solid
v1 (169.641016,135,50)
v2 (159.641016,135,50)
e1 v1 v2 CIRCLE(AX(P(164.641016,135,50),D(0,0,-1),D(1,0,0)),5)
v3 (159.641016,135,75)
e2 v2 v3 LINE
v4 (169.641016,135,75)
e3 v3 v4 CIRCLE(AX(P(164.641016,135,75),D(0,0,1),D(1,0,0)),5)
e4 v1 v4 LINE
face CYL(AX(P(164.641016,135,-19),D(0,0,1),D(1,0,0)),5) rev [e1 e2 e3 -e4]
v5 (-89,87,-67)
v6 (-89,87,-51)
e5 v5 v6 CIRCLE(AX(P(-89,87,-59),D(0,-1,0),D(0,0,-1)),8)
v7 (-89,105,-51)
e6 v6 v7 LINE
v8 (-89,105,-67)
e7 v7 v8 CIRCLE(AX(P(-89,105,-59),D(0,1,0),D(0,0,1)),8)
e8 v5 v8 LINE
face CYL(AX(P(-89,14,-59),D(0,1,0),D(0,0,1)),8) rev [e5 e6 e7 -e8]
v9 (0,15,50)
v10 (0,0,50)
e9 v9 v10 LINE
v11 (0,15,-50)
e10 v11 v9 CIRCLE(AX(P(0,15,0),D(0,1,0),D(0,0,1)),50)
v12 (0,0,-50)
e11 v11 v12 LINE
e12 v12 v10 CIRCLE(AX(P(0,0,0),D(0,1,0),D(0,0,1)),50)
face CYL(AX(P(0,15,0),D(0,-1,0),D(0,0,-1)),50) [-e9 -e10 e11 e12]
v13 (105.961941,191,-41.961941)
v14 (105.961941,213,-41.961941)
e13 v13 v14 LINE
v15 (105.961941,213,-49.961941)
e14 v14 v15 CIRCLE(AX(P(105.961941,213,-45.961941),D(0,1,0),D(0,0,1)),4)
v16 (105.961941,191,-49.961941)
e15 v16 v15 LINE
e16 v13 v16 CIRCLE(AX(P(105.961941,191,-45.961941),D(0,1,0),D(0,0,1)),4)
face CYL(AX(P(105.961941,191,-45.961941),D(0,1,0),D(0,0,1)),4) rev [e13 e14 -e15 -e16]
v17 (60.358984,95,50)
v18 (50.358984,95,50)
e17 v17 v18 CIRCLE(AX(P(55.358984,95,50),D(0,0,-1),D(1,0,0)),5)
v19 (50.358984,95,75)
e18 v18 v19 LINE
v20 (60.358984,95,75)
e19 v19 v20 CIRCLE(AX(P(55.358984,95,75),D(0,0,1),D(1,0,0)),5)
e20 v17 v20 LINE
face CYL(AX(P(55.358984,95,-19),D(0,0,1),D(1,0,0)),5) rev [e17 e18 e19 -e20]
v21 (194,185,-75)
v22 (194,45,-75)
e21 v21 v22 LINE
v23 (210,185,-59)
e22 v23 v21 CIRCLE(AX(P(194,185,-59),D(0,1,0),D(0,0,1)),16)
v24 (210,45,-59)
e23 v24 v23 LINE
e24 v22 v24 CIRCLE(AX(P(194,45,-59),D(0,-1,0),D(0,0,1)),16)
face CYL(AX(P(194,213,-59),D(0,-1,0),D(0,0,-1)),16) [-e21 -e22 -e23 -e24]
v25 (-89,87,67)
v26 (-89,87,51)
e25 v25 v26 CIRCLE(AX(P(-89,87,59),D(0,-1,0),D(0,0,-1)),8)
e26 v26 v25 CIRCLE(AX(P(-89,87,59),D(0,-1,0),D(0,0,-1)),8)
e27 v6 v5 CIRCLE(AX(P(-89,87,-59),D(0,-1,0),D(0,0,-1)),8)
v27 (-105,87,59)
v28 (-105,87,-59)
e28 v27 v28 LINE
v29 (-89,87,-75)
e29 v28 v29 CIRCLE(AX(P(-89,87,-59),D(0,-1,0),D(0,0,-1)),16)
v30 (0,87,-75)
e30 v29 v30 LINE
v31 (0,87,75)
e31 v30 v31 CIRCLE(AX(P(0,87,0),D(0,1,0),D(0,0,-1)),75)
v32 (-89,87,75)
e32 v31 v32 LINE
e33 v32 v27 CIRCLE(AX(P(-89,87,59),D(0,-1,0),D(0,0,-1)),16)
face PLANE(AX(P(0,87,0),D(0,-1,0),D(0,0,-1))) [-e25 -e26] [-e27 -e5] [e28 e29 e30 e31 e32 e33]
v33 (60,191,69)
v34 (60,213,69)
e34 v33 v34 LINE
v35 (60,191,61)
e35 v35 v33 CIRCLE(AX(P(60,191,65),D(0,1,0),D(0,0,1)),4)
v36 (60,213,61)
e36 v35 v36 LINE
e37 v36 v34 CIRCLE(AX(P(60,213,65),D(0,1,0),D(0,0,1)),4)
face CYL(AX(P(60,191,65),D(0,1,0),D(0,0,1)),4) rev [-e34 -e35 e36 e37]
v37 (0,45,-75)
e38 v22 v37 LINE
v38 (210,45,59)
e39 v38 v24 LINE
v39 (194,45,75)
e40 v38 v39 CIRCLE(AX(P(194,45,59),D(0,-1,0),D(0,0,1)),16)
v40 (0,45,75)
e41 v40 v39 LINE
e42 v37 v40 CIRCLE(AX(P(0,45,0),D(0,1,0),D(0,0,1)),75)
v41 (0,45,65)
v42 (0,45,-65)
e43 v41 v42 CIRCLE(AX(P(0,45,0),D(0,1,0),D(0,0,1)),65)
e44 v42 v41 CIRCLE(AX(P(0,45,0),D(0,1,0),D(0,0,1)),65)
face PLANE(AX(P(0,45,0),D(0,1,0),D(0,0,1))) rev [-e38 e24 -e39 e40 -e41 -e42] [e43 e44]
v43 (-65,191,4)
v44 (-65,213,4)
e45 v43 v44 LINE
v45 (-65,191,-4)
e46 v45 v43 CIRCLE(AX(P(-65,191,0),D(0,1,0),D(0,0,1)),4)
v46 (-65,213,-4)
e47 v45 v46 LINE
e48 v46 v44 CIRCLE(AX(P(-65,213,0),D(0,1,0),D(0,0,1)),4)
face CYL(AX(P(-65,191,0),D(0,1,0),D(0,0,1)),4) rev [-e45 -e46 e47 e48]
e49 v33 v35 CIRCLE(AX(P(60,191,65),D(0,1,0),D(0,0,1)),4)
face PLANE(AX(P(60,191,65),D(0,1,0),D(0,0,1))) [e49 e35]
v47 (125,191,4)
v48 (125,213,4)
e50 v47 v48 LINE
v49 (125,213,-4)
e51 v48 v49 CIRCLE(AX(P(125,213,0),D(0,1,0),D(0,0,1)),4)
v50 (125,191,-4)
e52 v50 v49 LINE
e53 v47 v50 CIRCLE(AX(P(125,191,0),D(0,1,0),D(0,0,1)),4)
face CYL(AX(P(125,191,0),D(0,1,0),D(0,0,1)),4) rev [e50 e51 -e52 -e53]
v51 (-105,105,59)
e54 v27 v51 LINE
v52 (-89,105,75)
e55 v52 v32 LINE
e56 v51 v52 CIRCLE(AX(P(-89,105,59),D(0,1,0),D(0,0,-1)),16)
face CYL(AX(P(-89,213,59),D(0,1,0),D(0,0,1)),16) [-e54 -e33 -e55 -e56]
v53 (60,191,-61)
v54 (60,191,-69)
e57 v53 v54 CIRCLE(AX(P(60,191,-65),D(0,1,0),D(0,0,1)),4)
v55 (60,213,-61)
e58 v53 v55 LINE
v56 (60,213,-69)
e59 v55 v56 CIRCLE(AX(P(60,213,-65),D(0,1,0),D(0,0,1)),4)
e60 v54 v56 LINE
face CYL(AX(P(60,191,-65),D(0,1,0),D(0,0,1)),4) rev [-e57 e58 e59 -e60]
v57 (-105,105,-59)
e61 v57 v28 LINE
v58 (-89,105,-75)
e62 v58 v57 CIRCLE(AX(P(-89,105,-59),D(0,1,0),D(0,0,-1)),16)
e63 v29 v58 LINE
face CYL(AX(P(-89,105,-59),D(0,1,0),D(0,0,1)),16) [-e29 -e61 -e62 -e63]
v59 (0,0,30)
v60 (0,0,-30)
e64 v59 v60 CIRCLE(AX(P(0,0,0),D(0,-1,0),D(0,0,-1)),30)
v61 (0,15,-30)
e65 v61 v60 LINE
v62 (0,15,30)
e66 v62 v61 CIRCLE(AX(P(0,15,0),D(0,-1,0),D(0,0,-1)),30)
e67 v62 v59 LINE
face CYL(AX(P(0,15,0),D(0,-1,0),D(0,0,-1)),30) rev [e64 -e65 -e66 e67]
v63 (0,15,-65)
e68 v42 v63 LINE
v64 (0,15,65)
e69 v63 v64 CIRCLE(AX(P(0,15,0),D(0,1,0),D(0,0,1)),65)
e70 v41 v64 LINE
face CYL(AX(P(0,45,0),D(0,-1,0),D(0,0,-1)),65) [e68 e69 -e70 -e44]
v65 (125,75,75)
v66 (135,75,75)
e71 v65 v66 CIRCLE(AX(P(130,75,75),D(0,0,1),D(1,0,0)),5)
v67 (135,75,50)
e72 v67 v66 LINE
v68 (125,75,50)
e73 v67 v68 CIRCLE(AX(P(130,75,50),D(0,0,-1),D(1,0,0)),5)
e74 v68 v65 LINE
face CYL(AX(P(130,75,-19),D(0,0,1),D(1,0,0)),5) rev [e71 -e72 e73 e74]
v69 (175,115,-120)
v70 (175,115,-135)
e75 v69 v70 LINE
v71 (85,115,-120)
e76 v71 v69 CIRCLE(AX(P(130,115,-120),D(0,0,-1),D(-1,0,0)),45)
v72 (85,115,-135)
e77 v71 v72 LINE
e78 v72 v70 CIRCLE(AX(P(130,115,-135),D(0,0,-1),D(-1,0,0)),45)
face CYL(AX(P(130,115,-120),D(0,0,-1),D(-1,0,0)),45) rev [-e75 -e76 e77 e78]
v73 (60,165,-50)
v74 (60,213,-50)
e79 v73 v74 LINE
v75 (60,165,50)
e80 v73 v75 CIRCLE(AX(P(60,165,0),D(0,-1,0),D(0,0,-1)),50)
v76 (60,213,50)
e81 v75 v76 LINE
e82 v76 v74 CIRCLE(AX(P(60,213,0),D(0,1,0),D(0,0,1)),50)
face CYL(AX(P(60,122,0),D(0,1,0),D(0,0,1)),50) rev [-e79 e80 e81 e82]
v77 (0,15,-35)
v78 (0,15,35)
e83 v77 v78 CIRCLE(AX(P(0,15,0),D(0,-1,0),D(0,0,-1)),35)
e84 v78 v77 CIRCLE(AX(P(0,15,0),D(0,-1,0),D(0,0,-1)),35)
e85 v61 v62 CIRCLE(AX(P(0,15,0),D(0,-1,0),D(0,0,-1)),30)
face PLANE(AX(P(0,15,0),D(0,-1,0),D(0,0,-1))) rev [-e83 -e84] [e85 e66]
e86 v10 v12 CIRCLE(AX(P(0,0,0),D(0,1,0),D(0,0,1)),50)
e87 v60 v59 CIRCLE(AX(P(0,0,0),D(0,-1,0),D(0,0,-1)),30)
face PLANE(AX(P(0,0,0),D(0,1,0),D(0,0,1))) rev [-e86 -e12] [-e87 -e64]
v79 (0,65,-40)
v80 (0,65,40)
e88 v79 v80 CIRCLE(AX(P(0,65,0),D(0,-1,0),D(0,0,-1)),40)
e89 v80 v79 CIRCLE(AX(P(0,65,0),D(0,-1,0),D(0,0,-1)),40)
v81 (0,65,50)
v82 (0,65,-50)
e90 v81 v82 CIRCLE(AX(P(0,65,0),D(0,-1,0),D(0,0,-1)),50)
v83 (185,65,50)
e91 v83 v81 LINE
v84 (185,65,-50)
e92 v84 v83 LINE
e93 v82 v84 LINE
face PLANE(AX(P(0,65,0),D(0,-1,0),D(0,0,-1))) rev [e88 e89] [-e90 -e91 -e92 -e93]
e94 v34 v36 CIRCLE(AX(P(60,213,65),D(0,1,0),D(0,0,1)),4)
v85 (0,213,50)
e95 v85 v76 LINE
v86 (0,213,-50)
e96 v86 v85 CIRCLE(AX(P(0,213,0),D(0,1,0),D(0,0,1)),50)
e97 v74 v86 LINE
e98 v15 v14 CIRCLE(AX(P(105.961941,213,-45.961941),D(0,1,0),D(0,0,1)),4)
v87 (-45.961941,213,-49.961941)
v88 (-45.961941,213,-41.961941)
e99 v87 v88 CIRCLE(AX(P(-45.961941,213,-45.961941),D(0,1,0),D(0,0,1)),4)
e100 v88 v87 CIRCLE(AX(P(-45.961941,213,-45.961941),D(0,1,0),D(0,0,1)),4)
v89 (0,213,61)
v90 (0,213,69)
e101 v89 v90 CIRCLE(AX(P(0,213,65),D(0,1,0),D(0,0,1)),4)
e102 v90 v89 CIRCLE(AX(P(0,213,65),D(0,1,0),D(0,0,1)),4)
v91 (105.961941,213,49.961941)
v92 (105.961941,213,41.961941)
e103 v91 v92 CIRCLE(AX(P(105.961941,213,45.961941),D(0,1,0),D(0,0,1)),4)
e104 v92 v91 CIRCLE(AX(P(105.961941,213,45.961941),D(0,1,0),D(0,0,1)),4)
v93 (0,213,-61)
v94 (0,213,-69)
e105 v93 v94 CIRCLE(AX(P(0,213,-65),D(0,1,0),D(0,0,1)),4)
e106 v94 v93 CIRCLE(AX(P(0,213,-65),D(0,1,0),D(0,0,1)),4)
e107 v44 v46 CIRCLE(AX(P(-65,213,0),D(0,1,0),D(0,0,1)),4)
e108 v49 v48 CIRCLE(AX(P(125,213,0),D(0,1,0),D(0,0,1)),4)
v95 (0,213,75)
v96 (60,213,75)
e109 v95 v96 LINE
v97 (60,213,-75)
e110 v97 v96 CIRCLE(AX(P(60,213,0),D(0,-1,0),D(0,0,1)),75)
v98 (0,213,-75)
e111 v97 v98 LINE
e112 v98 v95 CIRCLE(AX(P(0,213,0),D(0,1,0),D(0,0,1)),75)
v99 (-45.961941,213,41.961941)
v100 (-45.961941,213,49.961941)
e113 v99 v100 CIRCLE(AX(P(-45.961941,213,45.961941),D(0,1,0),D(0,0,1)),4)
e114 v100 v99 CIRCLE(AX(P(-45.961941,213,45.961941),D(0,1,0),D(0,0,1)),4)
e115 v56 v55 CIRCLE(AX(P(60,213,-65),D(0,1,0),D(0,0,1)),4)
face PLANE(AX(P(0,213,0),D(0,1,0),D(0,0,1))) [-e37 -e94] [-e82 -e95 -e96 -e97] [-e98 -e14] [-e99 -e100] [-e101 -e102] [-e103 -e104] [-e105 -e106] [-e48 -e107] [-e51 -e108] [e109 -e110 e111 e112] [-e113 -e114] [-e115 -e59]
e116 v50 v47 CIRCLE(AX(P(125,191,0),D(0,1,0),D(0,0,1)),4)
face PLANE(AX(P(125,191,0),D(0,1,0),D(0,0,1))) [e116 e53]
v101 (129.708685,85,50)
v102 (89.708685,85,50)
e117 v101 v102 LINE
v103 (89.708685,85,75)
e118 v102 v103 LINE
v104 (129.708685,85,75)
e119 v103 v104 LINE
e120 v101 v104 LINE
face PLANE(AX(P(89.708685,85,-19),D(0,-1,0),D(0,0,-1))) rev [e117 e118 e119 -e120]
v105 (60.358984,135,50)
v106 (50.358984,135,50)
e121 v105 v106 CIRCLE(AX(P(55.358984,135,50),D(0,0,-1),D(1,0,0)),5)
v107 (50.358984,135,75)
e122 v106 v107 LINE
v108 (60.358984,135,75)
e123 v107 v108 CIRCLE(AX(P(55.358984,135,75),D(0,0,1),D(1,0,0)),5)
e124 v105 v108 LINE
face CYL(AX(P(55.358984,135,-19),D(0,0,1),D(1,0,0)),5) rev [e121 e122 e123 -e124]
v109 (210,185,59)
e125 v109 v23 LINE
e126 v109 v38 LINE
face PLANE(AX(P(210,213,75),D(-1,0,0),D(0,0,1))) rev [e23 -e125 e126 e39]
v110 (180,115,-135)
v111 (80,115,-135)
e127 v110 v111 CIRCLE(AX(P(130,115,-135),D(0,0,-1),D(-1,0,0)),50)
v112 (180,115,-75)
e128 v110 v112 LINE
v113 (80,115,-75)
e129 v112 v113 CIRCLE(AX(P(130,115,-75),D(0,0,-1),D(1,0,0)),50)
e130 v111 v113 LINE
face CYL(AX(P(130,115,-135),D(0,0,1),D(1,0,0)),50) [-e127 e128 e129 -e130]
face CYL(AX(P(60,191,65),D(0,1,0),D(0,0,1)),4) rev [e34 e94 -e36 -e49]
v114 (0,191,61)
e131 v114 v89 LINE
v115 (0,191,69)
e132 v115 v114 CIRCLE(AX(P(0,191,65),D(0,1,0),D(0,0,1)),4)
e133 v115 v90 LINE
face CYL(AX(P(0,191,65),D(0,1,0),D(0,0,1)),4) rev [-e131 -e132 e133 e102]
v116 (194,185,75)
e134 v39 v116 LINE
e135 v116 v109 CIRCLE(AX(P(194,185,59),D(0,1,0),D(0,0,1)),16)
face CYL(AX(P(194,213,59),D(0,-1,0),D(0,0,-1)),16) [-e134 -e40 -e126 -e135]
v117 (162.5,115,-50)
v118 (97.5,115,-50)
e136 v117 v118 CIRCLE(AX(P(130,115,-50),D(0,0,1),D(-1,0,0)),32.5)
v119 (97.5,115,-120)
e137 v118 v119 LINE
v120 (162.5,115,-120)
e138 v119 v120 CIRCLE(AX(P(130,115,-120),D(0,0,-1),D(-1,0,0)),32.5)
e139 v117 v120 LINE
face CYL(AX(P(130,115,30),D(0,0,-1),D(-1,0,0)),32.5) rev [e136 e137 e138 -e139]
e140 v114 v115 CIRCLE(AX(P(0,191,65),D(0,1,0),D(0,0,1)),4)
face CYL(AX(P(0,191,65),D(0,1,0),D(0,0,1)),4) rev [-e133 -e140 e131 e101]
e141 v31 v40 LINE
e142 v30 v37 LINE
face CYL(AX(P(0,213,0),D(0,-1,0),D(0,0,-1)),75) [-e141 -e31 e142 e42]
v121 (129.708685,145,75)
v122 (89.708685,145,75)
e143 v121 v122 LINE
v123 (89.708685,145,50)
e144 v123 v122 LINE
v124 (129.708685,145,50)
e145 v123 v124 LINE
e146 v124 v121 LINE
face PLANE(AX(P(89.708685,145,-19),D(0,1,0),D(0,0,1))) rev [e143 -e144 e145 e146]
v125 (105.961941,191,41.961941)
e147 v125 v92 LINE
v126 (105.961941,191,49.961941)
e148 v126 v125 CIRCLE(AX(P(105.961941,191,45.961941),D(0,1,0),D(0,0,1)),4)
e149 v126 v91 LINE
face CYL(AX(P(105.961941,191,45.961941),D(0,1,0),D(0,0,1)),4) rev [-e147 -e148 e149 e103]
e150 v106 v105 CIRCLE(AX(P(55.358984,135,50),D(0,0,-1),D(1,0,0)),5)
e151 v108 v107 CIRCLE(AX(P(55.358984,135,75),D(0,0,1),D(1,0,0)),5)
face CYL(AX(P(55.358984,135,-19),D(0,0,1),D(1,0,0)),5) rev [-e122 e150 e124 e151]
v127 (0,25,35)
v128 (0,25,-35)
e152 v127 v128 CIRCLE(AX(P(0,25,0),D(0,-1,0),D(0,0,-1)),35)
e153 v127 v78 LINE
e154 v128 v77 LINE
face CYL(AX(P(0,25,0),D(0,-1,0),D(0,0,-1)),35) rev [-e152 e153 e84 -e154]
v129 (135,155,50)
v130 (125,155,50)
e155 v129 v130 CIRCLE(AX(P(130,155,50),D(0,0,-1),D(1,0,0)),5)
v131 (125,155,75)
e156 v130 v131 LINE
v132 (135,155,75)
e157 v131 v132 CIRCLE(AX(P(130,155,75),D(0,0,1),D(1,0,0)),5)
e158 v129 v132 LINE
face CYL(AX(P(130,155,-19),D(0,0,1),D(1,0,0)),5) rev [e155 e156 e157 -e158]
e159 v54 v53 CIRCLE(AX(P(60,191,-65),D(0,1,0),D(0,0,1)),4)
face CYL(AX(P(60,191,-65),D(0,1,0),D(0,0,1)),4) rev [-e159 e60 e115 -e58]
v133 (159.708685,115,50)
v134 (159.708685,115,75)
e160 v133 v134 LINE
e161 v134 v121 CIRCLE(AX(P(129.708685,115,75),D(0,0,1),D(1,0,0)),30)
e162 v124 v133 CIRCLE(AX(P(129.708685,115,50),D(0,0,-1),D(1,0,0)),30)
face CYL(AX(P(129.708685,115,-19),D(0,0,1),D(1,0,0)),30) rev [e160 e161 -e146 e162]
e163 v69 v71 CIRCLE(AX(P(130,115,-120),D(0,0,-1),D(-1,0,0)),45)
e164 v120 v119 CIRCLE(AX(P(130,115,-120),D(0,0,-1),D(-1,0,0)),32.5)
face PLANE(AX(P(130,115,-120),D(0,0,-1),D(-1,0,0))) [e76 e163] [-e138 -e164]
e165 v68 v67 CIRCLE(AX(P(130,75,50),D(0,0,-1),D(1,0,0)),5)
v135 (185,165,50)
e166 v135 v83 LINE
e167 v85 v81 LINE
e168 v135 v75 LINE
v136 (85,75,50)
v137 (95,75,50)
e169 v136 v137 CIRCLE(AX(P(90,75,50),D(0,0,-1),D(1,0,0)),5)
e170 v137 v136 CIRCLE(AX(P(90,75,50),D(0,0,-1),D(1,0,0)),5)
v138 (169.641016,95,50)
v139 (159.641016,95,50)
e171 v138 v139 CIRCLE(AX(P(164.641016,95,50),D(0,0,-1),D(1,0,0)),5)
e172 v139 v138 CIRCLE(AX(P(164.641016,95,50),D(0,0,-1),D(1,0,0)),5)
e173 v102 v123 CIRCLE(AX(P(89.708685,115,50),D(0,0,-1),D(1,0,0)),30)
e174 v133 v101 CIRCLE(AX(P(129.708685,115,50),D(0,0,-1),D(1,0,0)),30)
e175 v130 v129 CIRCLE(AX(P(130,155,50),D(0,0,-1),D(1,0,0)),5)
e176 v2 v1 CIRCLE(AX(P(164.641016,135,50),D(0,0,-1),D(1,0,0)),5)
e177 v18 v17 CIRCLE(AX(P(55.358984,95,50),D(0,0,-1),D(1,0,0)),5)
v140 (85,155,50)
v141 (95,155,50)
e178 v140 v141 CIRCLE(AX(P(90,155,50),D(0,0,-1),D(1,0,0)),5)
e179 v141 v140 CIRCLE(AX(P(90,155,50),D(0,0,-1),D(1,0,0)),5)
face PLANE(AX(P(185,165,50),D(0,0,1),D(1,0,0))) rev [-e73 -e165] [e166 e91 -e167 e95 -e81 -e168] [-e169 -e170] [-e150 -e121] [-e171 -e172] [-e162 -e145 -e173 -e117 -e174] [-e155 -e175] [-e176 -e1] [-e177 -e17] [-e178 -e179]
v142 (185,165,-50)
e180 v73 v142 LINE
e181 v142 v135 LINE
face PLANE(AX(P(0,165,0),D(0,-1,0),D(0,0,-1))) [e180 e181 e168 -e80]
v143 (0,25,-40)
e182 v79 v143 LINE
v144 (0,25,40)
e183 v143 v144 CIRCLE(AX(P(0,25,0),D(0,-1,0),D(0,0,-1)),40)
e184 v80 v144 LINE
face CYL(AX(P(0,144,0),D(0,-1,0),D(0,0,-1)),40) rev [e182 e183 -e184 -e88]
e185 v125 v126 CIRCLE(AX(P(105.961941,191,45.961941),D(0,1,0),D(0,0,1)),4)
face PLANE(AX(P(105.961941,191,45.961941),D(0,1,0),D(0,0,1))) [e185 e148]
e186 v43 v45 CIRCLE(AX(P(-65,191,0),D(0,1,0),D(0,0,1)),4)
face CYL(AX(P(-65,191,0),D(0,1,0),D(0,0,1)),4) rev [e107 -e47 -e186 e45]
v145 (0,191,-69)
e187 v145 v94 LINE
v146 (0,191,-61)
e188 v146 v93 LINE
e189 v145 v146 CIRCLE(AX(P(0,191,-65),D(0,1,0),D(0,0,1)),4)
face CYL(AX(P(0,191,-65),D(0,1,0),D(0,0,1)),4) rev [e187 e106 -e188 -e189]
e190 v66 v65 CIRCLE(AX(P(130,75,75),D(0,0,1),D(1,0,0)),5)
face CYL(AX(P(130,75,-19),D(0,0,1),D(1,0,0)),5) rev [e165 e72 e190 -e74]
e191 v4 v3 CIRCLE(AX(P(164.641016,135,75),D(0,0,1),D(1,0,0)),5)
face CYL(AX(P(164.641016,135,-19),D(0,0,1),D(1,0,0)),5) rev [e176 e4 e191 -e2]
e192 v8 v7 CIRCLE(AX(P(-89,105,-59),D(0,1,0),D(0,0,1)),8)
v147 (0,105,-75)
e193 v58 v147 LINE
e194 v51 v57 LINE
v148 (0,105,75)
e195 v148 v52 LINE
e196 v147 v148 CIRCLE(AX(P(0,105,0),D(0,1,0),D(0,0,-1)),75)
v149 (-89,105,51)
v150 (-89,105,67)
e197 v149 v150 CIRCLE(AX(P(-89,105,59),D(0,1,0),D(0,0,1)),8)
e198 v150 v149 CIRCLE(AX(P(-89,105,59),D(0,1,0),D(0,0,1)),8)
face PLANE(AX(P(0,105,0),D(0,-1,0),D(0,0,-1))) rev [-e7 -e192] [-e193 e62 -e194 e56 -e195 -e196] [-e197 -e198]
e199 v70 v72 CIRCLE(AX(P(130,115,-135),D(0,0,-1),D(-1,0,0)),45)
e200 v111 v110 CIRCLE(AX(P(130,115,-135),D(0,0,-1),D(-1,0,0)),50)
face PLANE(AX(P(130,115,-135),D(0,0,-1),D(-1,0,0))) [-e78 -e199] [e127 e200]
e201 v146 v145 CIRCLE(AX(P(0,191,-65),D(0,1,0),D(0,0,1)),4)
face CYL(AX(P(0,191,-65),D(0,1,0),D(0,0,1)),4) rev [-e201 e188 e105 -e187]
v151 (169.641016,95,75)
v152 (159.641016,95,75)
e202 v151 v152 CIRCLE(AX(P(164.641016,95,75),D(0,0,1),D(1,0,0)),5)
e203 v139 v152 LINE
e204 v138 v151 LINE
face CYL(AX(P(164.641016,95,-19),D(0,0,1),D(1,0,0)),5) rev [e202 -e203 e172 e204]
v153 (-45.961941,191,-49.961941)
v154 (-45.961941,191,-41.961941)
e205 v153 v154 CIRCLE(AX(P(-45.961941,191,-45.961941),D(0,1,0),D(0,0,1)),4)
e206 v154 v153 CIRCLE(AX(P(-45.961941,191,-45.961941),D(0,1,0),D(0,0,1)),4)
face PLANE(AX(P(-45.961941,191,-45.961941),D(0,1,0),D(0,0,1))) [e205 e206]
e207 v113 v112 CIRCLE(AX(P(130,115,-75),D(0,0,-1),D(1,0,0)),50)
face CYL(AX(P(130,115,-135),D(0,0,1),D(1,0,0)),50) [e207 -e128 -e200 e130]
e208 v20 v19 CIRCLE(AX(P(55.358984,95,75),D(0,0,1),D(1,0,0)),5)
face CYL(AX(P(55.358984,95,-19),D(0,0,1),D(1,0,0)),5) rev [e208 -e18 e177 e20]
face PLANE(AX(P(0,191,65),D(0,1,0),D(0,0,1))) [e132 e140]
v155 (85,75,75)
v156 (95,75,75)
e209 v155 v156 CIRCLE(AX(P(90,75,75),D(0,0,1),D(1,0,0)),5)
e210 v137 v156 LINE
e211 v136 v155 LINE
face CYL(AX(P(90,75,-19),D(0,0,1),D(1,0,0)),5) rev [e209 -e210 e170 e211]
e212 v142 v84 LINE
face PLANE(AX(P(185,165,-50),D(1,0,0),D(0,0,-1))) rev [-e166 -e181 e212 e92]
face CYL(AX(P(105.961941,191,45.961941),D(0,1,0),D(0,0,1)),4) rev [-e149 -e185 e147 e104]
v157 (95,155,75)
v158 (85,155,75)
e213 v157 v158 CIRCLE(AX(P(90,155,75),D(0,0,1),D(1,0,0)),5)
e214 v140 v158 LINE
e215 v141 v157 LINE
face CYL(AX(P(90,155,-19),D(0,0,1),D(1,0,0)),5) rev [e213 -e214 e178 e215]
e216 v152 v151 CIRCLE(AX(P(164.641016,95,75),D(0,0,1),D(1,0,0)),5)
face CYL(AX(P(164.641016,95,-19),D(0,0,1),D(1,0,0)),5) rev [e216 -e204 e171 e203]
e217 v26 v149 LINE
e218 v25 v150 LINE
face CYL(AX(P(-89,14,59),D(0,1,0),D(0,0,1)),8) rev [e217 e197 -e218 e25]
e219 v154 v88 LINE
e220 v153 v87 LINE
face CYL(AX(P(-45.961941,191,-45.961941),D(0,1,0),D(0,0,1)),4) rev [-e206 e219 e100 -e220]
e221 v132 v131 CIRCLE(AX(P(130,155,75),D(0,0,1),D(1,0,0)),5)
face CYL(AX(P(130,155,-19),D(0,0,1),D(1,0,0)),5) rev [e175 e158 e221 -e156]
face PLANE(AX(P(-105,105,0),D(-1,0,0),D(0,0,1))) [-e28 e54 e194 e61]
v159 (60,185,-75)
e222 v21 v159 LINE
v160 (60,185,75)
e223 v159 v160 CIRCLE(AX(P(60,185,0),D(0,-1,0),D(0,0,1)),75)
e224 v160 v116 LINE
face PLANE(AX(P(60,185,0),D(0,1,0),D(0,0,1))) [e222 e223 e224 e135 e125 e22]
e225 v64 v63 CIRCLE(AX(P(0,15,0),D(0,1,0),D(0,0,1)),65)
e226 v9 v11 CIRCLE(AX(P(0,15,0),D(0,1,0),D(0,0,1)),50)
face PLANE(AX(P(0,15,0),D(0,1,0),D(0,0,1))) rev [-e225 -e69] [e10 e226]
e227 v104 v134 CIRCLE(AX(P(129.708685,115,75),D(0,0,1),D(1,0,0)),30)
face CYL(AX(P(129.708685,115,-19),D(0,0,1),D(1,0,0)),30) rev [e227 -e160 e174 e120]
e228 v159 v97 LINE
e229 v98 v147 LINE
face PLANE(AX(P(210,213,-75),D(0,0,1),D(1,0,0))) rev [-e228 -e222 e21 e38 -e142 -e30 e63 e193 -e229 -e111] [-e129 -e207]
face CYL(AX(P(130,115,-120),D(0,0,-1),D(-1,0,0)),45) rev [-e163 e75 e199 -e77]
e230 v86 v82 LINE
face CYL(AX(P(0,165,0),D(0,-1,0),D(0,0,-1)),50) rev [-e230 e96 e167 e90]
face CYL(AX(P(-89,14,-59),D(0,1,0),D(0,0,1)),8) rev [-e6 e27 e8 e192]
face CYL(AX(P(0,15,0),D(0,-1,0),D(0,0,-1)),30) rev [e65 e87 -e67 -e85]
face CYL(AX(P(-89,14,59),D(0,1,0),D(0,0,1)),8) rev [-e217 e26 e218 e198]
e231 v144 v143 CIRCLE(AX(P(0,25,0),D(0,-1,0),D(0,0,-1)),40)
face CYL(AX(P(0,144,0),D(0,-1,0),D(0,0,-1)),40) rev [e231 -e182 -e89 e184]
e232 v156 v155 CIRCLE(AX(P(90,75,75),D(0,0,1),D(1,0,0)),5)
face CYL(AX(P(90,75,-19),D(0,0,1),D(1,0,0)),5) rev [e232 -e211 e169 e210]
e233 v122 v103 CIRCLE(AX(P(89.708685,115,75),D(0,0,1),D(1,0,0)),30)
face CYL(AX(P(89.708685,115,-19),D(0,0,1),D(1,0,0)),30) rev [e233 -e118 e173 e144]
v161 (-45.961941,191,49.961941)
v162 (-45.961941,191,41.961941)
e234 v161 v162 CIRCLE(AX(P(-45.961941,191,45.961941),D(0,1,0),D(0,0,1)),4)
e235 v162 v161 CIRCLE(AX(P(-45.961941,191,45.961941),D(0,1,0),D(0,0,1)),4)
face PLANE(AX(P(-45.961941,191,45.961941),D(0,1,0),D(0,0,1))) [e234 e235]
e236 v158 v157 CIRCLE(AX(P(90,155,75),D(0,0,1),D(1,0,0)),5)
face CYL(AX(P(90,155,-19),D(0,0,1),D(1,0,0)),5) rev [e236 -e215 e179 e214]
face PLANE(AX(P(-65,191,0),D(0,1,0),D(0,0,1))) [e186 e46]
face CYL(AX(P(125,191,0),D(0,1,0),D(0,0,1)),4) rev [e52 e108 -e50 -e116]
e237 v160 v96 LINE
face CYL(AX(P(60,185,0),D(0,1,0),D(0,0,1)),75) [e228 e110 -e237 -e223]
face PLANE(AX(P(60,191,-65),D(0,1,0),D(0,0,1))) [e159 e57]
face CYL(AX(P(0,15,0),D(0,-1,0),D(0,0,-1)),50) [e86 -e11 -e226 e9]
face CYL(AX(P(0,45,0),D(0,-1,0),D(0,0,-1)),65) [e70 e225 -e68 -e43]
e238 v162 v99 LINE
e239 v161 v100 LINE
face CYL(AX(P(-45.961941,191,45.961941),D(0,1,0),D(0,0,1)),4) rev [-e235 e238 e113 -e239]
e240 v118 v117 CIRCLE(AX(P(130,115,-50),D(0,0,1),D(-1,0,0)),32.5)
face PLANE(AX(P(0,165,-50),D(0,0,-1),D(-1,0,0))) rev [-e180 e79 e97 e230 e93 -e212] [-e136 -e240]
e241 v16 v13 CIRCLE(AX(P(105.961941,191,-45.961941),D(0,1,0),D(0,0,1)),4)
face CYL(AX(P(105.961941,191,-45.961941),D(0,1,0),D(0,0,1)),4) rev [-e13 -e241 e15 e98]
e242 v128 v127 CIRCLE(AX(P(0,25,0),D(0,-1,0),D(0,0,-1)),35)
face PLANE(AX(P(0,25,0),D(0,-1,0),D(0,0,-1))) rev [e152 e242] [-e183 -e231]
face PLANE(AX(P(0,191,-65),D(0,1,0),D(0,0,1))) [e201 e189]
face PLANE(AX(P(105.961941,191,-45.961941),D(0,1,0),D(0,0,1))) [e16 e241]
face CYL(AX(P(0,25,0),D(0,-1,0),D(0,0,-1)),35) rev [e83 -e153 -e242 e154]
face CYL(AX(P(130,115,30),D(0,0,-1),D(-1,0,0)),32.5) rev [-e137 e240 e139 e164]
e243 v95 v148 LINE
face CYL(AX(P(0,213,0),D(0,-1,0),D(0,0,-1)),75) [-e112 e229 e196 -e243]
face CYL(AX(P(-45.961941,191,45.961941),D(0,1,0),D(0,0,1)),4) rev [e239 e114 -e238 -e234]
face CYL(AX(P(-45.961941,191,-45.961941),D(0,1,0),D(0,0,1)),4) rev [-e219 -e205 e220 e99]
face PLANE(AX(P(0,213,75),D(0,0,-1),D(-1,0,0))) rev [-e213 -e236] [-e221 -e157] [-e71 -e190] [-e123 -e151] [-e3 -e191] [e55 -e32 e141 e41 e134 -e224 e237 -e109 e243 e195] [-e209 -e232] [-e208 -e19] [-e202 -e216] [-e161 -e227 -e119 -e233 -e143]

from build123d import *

# Parameters (mm, degrees)
BASE_BOSS_SKETCH_R         = 50
BASE_BOSS_100_DEPTH        = 15
BEARING_BOSS_SKETCH_R      = 65
BEARING_BOSS_130_DEPTH     = 30
HOUSING_BLOCK_75X210_DEPTH = 168
HOUSING_RECESS_CUT_DEPTH   = 28
MOUNTING_FLANGE_DEPTH      = 18
GEAR_CAVITY_SKETCH_R       = 5
GEAR_CAVITY_CUT_DEPTH      = 94
CAVITY_RELIEF_CUT_DEPTH    = 94
PORT_BOSS_SKETCH_R         = 50
PORT_BOSS_100_DEPTH        = 60
PORT_COUNTERBORE_SKETCH_R  = 45
PORT_COUNTERBORE_90_DEPTH  = 15
PORT_BORE_SKETCH_R         = 32.5
PORT_BORE_65_DEPTH         = 150
SIDE_POCKET_50X185_DEPTH   = 50
BASE_BORE_SKETCH_R         = 30
BASE_BORE_60_DEPTH         = 15
BASE_COUNTERBORE_SKETCH_R  = 35
BASE_COUNTERBORE_70_DEPTH  = 10
SHAFT_BORE_SKETCH_R        = 40
SHAFT_BORE_80_DEPTH        = 119
COVER_BOLT_HOLES_SKETCH_R  = 4
COVER_BOLT_HOLES_8_DEPTH   = 22
FLANGE_FILLET_R16_A_R      = 16
FLANGE_FILLET_R16_B_R      = 16
FLANGE_BOLT_HOLES_SKETCH_R = 8
FLANGE_BOLT_HOLES_16_DEPTH = 91
INNER_START                = -91
INNER_SLOT_CUT_DEPTH       = 91
HOUSING_FILLET_R16_A_R     = 16
HOUSING_FILLET_R16_B_R     = 16


with BuildPart() as part:
    # Base Boss Sketch → Base Boss Ø100 (new body)
    with BuildSketch(Plane(origin=(0, 0, 0), x_dir=(1, 0, 0), z_dir=(0, 1, 0))):
        with Locations(Location((0, 0, 0), (0, 0, 270))):
            Circle(BASE_BOSS_SKETCH_R)
    extrude(amount=BASE_BOSS_100_DEPTH)

    # Bearing Boss Sketch → Bearing Boss Ø130 (add)
    with BuildSketch(Plane(origin=(0, 15, 0), x_dir=(1, 0, 0), z_dir=(0, 1, 0))):
        with Locations(Location((0, 0, 0), (0, 0, 270))):
            Circle(BEARING_BOSS_SKETCH_R)
    extrude(amount=BEARING_BOSS_130_DEPTH)

    # Housing Block Sketch → Housing Block 75x210 (add)
    with BuildSketch(Plane(origin=(0, 45, 0), x_dir=(1, 0, 0), z_dir=(0, 1, 0))):
        with BuildLine():
            Line((0, -75), (210, -75))
            Line((210, -75), (210, 75))
            Line((210, 75), (0, 75))
            ThreePointArc((0, 75), (-75, 0), (0, -75))
        make_face()
    extrude(amount=HOUSING_BLOCK_75X210_DEPTH)

    # Housing Recess Sketch → Housing Recess Cut (cut)
    with BuildSketch(Plane(origin=(0, 213, 0), x_dir=(1, 0, 0), z_dir=(0, 1, 0))):
        with BuildLine():
            Line((60, 75), (210, 75))
            Line((210, 75), (210, -75))
            Line((210, -75), (60, -75))
            ThreePointArc((60, -75), (135, 0), (60, 75))
        make_face()
    extrude(amount=-HOUSING_RECESS_CUT_DEPTH, mode=Mode.SUBTRACT)

    # Mounting Flange Sketch → Mounting Flange (add)
    with BuildSketch(Plane(origin=(0, 87, 0), x_dir=(-1, 0, 0), z_dir=(0, -1, 0))):
        with BuildLine():
            Line((105, 0), (105, 75))
            Line((105, 75), (0, 75))
            ThreePointArc((0, 75), (75, 0), (0, -75))
            Line((0, -75), (105, -75))
            Line((105, -75), (105, 0))
        make_face()
    extrude(amount=-MOUNTING_FLANGE_DEPTH)

    # Gear Cavity Sketch → Gear Cavity Cut (cut)
    with BuildSketch(Plane.XY.offset(75)):
        with Locations((130, 155)):
            Circle(GEAR_CAVITY_SKETCH_R)
        with Locations((90, 155)):
            Circle(GEAR_CAVITY_SKETCH_R)
        with Locations((164.641016151, 135)):
            Circle(GEAR_CAVITY_SKETCH_R)
        with Locations((164.641016151, 95)):
            Circle(GEAR_CAVITY_SKETCH_R)
        with Locations((130, 75)):
            Circle(GEAR_CAVITY_SKETCH_R)
        with Locations((90, 75)):
            Circle(GEAR_CAVITY_SKETCH_R)
        with Locations((55.358983849, 95)):
            Circle(GEAR_CAVITY_SKETCH_R)
        with Locations((55.358983849, 135)):
            Circle(GEAR_CAVITY_SKETCH_R)
    extrude(amount=-GEAR_CAVITY_CUT_DEPTH, mode=Mode.SUBTRACT)

    # Cavity Relief Sketch → Cavity Relief Cut (cut)
    with BuildSketch(Plane.XY.offset(75)):
        with BuildLine():
            Line((89.708684664, 145), (129.708684664, 145))
            ThreePointArc((129.708684664, 145), (159.708684664, 115), (129.708684664, 85))
            Line((129.708684664, 85), (89.708684664, 85))
            ThreePointArc((89.708684664, 85), (59.708684664, 115), (89.708684664, 145))
        make_face()
    extrude(amount=-CAVITY_RELIEF_CUT_DEPTH, mode=Mode.SUBTRACT)

    # Port Boss Sketch → Port Boss Ø100 (add)
    with BuildSketch(Plane(origin=(0, 0, -75), x_dir=(-1, 0, 0), z_dir=(0, 0, -1))):
        with Locations(Location((-130, 115, 0), (0, 0, 180))):
            Circle(PORT_BOSS_SKETCH_R)
    extrude(amount=PORT_BOSS_100_DEPTH)

    # Port Counterbore Sketch → Port Counterbore Ø90 (cut)
    with BuildSketch(Plane(origin=(0, 0, -135), x_dir=(-1, 0, 0), z_dir=(0, 0, -1))):
        with Locations((-130, 115)):
            Circle(PORT_COUNTERBORE_SKETCH_R)
    extrude(amount=-PORT_COUNTERBORE_90_DEPTH, mode=Mode.SUBTRACT)

    # Port Bore Sketch → Port Bore Ø65 (cut)
    with BuildSketch(Plane(origin=(0, 0, -120), x_dir=(-1, 0, 0), z_dir=(0, 0, -1))):
        with Locations((-130, 115)):
            Circle(PORT_BORE_SKETCH_R)
    extrude(amount=-PORT_BORE_65_DEPTH, mode=Mode.SUBTRACT)

    # Side Pocket Sketch → Side Pocket 50x185 (cut, symmetric)
    with BuildSketch(Plane(origin=(0, 115, 0), x_dir=(-1, 0, 0), z_dir=(0, -1, 0))):
        with BuildLine():
            Line((0, 50), (-185, 50))
            Line((-185, 50), (-185, -50))
            Line((-185, -50), (0, -50))
            ThreePointArc((0, -50), (50, 0), (0, 50))
        make_face()
    extrude(amount=SIDE_POCKET_50X185_DEPTH, both=True, mode=Mode.SUBTRACT)

    # Base Bore Sketch → Base Bore Ø60 (cut)
    with BuildSketch(Plane.XZ):
        with Locations(Location((0, 0, 0), (0, 0, 270))):
            Circle(BASE_BORE_SKETCH_R)
    extrude(amount=-BASE_BORE_60_DEPTH, mode=Mode.SUBTRACT)

    # Base Counterbore Sketch → Base Counterbore Ø70 (cut)
    with BuildSketch(Plane.XZ.offset(-15)):
        with Locations(Location((0, 0, 0), (0, 0, 270))):
            Circle(BASE_COUNTERBORE_SKETCH_R)
    extrude(amount=-BASE_COUNTERBORE_70_DEPTH, mode=Mode.SUBTRACT)

    # Shaft Bore Sketch → Shaft Bore Ø80 (cut)
    with BuildSketch(Plane.XZ.offset(-25)):
        with Locations(Location((0, 0, 0), (0, 0, 270))):
            Circle(SHAFT_BORE_SKETCH_R)
    extrude(amount=-SHAFT_BORE_80_DEPTH, mode=Mode.SUBTRACT)

    # Cover Bolt Holes Sketch → Cover Bolt Holes Ø8 (cut)
    with BuildSketch(Plane(origin=(0, 213, 0), x_dir=(1, 0, 0), z_dir=(0, 1, 0))):
        with Locations(Location((125, 0, 0), (0, 0, 270))):
            Circle(COVER_BOLT_HOLES_SKETCH_R)
        with Locations(Location((105.961940777, 45.961940777, 0), (0, 0, 270))):
            Circle(COVER_BOLT_HOLES_SKETCH_R)
        with Locations(Location((105.961940777, -45.961940777, 0), (0, 0, 270))):
            Circle(COVER_BOLT_HOLES_SKETCH_R)
        with Locations(Location((60, -65, 0), (0, 0, 270))):
            Circle(COVER_BOLT_HOLES_SKETCH_R)
        with Locations(Location((0, -65, 0), (0, 0, 270))):
            Circle(COVER_BOLT_HOLES_SKETCH_R)
        with Locations(Location((-45.961940777, -45.961940777, 0), (0, 0, 270))):
            Circle(COVER_BOLT_HOLES_SKETCH_R)
        with Locations(Location((-45.961940777, 45.961940777, 0), (0, 0, 270))):
            Circle(COVER_BOLT_HOLES_SKETCH_R)
        with Locations(Location((0, 65, 0), (0, 0, 270))):
            Circle(COVER_BOLT_HOLES_SKETCH_R)
        with Locations(Location((60, 65, 0), (0, 0, 270))):
            Circle(COVER_BOLT_HOLES_SKETCH_R)
        with Locations(Location((-65, 0, 0), (0, 0, 270))):
            Circle(COVER_BOLT_HOLES_SKETCH_R)
    extrude(amount=-COVER_BOLT_HOLES_8_DEPTH, mode=Mode.SUBTRACT)

    # Flange Fillet R16 A
    flange_fillet_r16_a_edges = [part.edges().sort_by_distance(p)[0] for p in [
        (-105, 96, 75),
    ]]
    fillet(flange_fillet_r16_a_edges, radius=FLANGE_FILLET_R16_A_R)

    # Flange Fillet R16 B
    flange_fillet_r16_b_edges = [part.edges().sort_by_distance(p)[0] for p in [
        (-105, 96, -75),
    ]]
    fillet(flange_fillet_r16_b_edges, radius=FLANGE_FILLET_R16_B_R)

    # Flange Bolt Holes Sketch → Flange Bolt Holes Ø16 (cut)
    with BuildSketch(Plane(origin=(0, 105, 0), x_dir=(1, 0, 0), z_dir=(0, 1, 0))):
        with Locations(Location((-89, 59, 0), (0, 0, 270))):
            Circle(FLANGE_BOLT_HOLES_SKETCH_R)
        with Locations(Location((-89, -59, 0), (0, 0, 270))):
            Circle(FLANGE_BOLT_HOLES_SKETCH_R)
    extrude(amount=-FLANGE_BOLT_HOLES_16_DEPTH, mode=Mode.SUBTRACT)

    # Inner Slot Sketch → Inner Slot Cut (cut)
    with BuildSketch(Plane(origin=(0, 213, 0), x_dir=(1, 0, 0), z_dir=(0, 1, 0)).offset(INNER_START)):
        with BuildLine():
            Line((60, -50), (0, -50))
            ThreePointArc((0, -50), (-50, 0), (0, 50))
            Line((0, 50), (60, 50))
            ThreePointArc((60, 50), (110, 0), (60, -50))
        make_face()
    extrude(amount=INNER_SLOT_CUT_DEPTH, mode=Mode.SUBTRACT)

    # Housing Fillet R16 A
    housing_fillet_r16_a_edges = [part.edges().sort_by_distance(p)[0] for p in [
        (210, 115, -75),
    ]]
    fillet(housing_fillet_r16_a_edges, radius=HOUSING_FILLET_R16_A_R)

    # Housing Fillet R16 B
    housing_fillet_r16_b_edges = [part.edges().sort_by_distance(p)[0] for p in [
        (210, 115, 75),
    ]]
    fillet(housing_fillet_r16_b_edges, radius=HOUSING_FILLET_R16_B_R)


solid = part.part
